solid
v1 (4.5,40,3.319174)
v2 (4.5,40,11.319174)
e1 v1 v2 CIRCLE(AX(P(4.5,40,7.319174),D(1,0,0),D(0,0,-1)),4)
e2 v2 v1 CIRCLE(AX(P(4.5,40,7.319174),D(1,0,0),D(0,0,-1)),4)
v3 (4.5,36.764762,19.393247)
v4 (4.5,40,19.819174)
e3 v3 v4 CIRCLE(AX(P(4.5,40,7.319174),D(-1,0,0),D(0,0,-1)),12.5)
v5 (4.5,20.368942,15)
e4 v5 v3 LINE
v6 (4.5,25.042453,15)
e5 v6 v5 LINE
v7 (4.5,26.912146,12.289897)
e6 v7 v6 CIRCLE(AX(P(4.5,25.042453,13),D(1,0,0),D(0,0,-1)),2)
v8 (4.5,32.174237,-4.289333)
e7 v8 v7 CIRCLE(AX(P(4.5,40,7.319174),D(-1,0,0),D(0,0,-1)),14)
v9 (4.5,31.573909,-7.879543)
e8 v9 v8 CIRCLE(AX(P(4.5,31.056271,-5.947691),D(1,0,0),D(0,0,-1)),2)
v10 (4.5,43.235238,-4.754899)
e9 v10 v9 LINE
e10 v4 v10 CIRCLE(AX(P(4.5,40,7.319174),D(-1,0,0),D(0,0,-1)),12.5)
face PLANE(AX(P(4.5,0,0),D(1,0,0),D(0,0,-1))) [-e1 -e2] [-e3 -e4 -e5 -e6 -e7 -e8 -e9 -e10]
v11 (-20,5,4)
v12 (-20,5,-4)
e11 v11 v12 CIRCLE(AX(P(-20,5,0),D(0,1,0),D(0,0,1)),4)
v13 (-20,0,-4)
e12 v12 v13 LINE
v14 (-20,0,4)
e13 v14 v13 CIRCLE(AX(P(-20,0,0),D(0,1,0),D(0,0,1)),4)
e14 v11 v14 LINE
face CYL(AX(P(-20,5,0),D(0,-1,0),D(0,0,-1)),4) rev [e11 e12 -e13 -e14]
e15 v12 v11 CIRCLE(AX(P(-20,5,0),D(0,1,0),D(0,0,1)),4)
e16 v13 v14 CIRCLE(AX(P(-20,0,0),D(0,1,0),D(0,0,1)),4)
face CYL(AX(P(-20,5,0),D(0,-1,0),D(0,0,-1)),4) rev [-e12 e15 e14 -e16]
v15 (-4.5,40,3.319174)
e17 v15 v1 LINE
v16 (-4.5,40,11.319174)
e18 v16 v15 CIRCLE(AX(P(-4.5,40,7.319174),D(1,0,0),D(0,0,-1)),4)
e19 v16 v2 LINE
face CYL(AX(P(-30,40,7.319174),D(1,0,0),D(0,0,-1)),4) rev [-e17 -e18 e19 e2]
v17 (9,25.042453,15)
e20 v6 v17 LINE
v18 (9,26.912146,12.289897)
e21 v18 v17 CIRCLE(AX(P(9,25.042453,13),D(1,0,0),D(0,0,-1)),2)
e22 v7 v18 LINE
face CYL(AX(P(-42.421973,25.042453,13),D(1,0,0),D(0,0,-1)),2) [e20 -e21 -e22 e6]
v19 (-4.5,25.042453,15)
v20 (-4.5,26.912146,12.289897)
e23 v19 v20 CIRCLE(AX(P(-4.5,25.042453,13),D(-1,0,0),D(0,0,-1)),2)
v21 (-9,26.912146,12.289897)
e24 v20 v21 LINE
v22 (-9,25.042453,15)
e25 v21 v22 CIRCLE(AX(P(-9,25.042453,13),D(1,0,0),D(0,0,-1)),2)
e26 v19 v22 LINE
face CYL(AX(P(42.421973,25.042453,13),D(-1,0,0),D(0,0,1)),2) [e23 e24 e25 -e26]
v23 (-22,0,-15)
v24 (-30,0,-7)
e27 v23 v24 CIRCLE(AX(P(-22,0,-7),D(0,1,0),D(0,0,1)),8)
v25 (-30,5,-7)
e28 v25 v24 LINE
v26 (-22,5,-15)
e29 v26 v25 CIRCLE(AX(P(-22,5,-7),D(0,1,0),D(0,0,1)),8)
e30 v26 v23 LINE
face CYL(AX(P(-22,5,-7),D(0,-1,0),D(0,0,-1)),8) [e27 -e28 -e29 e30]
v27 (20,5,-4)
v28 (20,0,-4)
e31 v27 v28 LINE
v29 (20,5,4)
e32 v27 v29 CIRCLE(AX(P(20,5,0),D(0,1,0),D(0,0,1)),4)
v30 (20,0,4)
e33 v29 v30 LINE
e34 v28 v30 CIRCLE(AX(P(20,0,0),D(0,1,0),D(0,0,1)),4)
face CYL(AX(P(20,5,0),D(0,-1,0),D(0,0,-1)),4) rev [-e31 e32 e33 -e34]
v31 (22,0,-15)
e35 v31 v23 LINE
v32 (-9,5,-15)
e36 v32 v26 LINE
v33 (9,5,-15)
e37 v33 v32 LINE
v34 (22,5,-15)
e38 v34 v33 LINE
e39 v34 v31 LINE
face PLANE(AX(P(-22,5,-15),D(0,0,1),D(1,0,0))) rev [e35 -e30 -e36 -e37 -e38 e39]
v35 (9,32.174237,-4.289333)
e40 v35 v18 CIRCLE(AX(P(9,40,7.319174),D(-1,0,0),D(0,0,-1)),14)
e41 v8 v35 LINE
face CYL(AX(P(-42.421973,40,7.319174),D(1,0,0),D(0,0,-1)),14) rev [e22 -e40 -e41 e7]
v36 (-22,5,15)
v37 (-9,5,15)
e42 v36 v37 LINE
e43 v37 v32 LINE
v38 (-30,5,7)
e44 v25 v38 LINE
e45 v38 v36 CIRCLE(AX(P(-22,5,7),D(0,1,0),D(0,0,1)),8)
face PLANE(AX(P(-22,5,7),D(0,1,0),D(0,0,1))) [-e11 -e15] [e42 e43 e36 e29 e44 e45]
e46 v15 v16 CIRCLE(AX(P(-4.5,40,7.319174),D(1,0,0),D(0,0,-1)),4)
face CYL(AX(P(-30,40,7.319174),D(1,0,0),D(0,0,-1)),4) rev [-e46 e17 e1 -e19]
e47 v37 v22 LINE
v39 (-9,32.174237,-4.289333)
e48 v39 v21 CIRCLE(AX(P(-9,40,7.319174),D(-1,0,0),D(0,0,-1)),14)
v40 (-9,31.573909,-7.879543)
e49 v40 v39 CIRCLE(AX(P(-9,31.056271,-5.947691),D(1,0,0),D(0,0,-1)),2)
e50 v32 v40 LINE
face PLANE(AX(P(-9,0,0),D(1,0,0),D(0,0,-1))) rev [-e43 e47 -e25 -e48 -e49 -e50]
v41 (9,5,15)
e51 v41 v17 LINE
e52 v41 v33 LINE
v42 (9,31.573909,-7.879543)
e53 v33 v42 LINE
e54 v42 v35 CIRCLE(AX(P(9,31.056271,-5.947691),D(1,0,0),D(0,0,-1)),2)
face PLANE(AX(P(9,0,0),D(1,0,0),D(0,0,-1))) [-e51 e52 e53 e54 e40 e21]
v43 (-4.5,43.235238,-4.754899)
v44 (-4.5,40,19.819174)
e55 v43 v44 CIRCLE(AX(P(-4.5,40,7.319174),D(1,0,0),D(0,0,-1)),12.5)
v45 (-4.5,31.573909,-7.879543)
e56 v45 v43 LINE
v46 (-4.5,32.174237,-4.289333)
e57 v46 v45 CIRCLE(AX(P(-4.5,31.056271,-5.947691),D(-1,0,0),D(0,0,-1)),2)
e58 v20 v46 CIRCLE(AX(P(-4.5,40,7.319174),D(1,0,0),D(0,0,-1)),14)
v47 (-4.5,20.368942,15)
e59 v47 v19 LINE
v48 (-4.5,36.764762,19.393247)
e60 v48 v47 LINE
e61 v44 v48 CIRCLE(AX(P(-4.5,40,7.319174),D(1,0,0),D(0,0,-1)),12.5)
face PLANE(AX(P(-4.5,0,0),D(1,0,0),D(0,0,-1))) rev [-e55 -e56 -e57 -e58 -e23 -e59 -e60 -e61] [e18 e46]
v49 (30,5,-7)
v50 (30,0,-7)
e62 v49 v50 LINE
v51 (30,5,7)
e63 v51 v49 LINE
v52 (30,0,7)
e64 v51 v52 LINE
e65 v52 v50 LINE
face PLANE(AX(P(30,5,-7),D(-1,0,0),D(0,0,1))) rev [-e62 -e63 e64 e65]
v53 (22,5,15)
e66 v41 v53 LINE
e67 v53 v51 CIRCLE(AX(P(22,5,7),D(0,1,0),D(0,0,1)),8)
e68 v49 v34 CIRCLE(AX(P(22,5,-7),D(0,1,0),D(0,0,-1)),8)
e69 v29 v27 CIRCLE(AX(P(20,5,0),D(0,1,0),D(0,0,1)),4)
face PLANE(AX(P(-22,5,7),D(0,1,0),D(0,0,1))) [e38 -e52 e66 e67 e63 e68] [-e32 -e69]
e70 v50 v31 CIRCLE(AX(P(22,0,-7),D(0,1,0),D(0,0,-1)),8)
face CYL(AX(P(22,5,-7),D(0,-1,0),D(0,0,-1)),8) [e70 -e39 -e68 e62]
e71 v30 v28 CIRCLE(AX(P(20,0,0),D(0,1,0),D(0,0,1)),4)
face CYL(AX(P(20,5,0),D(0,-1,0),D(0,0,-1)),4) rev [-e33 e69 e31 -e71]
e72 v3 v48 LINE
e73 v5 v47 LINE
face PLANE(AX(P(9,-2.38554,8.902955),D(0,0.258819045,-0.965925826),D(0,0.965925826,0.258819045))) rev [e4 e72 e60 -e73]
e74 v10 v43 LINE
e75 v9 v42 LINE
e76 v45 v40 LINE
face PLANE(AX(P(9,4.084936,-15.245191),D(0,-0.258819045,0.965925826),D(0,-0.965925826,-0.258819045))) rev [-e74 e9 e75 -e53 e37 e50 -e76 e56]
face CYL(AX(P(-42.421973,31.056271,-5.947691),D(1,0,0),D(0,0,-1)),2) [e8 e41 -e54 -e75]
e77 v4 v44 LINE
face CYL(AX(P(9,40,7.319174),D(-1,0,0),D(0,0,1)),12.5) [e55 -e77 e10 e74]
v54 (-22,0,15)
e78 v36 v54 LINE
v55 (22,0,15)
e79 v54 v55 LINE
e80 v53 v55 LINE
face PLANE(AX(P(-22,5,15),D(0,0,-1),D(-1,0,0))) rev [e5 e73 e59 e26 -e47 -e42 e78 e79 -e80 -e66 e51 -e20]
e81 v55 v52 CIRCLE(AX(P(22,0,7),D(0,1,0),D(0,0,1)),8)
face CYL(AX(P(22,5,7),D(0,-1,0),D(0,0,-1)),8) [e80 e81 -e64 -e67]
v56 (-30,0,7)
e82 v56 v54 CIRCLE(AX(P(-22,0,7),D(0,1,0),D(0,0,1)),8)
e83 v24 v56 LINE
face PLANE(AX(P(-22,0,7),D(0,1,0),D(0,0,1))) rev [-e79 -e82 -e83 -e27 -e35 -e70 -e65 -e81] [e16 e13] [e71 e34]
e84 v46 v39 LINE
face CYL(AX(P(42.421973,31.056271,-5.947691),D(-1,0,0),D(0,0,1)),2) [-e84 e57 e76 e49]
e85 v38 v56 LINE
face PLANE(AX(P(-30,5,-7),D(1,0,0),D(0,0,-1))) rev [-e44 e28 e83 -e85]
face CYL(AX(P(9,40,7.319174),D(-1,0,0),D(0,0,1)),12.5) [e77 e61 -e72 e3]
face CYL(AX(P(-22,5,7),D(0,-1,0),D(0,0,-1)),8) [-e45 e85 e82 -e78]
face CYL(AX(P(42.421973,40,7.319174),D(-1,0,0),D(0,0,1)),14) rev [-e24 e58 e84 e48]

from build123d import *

# Parameters (mm, degrees)
BASE_PLATE_SKETCH_R       = 4
BASE_PLATE_DEPTH          = 5
TAPERED_UPRIGHT_DEPTH     = 9
PIVOT_LUG_DEPTH           = 10
LUG_SIDE_RELIEF_CUT_DEPTH = 5.5
PIVOT_BORE_SKETCH_R       = 4
PIVOT_BORE_8_DEPTH        = 66.873360759


with BuildPart() as part:
    # Base Plate Sketch → Base Plate (new body)
    with BuildSketch(Plane(origin=(0, 0, 0), x_dir=(1, 0, 0), z_dir=(0, 1, 0))):
        with BuildLine():
            Line((-22, 15), (22, 15))
            ThreePointArc((22, 15), (27.656854249, 12.656854249), (30, 7))
            Line((30, 7), (30, -7))
            ThreePointArc((30, -7), (27.656854249, -12.656854249), (22, -15))
            Line((22, -15), (-22, -15))
            ThreePointArc((-22, -15), (-27.656854249, -12.656854249), (-30, -7))
            Line((-30, -7), (-30, 7))
            ThreePointArc((-30, 7), (-27.656854249, 12.656854249), (-22, 15))
        make_face()
        with Locations(Location((-20, 0, 0), (0, 0, 270))):
            Circle(BASE_PLATE_SKETCH_R, mode=Mode.SUBTRACT)
        with Locations(Location((20, 0, 0), (0, 0, 270))):
            Circle(BASE_PLATE_SKETCH_R, mode=Mode.SUBTRACT)
    extrude(amount=BASE_PLATE_DEPTH)

    # Tapered Upright Sketch → Tapered Upright (add, symmetric)
    with BuildSketch(Plane(origin=(0, 0, 0), x_dir=(0, 0, -1), z_dir=(1, 0, 0))):
        with BuildLine():
            Line((-15, 20.368941598), (-15, 5))
            Line((-15, 5), (15, 5))
            Line((15, 5), (4.754898838, 43.235238064))
            ThreePointArc((4.754898838, 43.235238064), (-10.554412054, 52.074072829), (-19.393246819, 36.764761936))
            Line((-19.393246819, 36.764761936), (-15, 20.368941598))
        make_face()
    extrude(amount=TAPERED_UPRIGHT_DEPTH, both=True)

    # Pivot Lug Sketch → Pivot Lug (add, symmetric)
    with BuildSketch(Plane(origin=(0, 0, 0), x_dir=(0, 0, -1), z_dir=(1, 0, 0))):
        with BuildLine():
            Line((-15, 20.368941598), (-15, 25.04245288))
            ThreePointArc((-15, 25.04245288), (-14.135736214, 26.688692003), (-12.289896749, 26.91214627))
            ThreePointArc((-12.289896749, 26.91214627), (-3.083912061, 26.655991742), (4.289332839, 32.17423683))
            ThreePointArc((4.289332839, 32.17423683), (6.27753657, 33.028883618), (7.87954261, 31.573908753))
            Line((7.87954261, 31.573908753), (4.754898838, 43.235238064))
            ThreePointArc((4.754898838, 43.235238064), (-10.554412054, 52.074072829), (-19.393246819, 36.764761936))
            Line((-19.393246819, 36.764761936), (-15, 20.368941598))
        make_face()
    extrude(amount=PIVOT_LUG_DEPTH, both=True)

    # Lug Side Relief Sketch → Lug Side Relief Cut (cut)
    with BuildSketch(Plane(origin=(10, 0, 0), x_dir=(0, 0, -1), z_dir=(1, 0, 0))):
        with BuildLine():
            Line((-19.393246819, 36.764761936), (-15, 20.368941598))
            Line((-15, 20.368941598), (-15, 25.04245288))
            ThreePointArc((-15, 25.04245288), (-14.135736214, 26.688692003), (-12.289896749, 26.91214627))
            ThreePointArc((-12.289896749, 26.91214627), (-3.083912061, 26.655991742), (4.289332839, 32.17423683))
            ThreePointArc((4.289332839, 32.17423683), (6.27753657, 33.028883618), (7.87954261, 31.573908753))
            Line((7.87954261, 31.573908753), (4.754898838, 43.235238064))
            ThreePointArc((4.754898838, 43.235238064), (-10.554412054, 52.074072829), (-19.393246819, 36.764761936))
        make_face()
    lug_side_relief_cut = extrude(amount=-LUG_SIDE_RELIEF_CUT_DEPTH, mode=Mode.SUBTRACT)

    # Lug Side Relief Mirror: Lug Side Relief Cut across plane
    add(lug_side_relief_cut.mirror(Plane(origin=(0, 0, 0), x_dir=(0, 0, 1), z_dir=(1, 0, 0))), mode=Mode.SUBTRACT)

    # Pivot Bore Sketch → Pivot Bore Ø8 (cut, through all)
    with BuildSketch(Plane(origin=(4.5, 0, 0), x_dir=(0, 0, -1), z_dir=(1, 0, 0))):
        with Locations((-7.31917399, 40)):
            Circle(PIVOT_BORE_SKETCH_R)
    extrude(amount=-PIVOT_BORE_8_DEPTH, mode=Mode.SUBTRACT)


solid = part.part
